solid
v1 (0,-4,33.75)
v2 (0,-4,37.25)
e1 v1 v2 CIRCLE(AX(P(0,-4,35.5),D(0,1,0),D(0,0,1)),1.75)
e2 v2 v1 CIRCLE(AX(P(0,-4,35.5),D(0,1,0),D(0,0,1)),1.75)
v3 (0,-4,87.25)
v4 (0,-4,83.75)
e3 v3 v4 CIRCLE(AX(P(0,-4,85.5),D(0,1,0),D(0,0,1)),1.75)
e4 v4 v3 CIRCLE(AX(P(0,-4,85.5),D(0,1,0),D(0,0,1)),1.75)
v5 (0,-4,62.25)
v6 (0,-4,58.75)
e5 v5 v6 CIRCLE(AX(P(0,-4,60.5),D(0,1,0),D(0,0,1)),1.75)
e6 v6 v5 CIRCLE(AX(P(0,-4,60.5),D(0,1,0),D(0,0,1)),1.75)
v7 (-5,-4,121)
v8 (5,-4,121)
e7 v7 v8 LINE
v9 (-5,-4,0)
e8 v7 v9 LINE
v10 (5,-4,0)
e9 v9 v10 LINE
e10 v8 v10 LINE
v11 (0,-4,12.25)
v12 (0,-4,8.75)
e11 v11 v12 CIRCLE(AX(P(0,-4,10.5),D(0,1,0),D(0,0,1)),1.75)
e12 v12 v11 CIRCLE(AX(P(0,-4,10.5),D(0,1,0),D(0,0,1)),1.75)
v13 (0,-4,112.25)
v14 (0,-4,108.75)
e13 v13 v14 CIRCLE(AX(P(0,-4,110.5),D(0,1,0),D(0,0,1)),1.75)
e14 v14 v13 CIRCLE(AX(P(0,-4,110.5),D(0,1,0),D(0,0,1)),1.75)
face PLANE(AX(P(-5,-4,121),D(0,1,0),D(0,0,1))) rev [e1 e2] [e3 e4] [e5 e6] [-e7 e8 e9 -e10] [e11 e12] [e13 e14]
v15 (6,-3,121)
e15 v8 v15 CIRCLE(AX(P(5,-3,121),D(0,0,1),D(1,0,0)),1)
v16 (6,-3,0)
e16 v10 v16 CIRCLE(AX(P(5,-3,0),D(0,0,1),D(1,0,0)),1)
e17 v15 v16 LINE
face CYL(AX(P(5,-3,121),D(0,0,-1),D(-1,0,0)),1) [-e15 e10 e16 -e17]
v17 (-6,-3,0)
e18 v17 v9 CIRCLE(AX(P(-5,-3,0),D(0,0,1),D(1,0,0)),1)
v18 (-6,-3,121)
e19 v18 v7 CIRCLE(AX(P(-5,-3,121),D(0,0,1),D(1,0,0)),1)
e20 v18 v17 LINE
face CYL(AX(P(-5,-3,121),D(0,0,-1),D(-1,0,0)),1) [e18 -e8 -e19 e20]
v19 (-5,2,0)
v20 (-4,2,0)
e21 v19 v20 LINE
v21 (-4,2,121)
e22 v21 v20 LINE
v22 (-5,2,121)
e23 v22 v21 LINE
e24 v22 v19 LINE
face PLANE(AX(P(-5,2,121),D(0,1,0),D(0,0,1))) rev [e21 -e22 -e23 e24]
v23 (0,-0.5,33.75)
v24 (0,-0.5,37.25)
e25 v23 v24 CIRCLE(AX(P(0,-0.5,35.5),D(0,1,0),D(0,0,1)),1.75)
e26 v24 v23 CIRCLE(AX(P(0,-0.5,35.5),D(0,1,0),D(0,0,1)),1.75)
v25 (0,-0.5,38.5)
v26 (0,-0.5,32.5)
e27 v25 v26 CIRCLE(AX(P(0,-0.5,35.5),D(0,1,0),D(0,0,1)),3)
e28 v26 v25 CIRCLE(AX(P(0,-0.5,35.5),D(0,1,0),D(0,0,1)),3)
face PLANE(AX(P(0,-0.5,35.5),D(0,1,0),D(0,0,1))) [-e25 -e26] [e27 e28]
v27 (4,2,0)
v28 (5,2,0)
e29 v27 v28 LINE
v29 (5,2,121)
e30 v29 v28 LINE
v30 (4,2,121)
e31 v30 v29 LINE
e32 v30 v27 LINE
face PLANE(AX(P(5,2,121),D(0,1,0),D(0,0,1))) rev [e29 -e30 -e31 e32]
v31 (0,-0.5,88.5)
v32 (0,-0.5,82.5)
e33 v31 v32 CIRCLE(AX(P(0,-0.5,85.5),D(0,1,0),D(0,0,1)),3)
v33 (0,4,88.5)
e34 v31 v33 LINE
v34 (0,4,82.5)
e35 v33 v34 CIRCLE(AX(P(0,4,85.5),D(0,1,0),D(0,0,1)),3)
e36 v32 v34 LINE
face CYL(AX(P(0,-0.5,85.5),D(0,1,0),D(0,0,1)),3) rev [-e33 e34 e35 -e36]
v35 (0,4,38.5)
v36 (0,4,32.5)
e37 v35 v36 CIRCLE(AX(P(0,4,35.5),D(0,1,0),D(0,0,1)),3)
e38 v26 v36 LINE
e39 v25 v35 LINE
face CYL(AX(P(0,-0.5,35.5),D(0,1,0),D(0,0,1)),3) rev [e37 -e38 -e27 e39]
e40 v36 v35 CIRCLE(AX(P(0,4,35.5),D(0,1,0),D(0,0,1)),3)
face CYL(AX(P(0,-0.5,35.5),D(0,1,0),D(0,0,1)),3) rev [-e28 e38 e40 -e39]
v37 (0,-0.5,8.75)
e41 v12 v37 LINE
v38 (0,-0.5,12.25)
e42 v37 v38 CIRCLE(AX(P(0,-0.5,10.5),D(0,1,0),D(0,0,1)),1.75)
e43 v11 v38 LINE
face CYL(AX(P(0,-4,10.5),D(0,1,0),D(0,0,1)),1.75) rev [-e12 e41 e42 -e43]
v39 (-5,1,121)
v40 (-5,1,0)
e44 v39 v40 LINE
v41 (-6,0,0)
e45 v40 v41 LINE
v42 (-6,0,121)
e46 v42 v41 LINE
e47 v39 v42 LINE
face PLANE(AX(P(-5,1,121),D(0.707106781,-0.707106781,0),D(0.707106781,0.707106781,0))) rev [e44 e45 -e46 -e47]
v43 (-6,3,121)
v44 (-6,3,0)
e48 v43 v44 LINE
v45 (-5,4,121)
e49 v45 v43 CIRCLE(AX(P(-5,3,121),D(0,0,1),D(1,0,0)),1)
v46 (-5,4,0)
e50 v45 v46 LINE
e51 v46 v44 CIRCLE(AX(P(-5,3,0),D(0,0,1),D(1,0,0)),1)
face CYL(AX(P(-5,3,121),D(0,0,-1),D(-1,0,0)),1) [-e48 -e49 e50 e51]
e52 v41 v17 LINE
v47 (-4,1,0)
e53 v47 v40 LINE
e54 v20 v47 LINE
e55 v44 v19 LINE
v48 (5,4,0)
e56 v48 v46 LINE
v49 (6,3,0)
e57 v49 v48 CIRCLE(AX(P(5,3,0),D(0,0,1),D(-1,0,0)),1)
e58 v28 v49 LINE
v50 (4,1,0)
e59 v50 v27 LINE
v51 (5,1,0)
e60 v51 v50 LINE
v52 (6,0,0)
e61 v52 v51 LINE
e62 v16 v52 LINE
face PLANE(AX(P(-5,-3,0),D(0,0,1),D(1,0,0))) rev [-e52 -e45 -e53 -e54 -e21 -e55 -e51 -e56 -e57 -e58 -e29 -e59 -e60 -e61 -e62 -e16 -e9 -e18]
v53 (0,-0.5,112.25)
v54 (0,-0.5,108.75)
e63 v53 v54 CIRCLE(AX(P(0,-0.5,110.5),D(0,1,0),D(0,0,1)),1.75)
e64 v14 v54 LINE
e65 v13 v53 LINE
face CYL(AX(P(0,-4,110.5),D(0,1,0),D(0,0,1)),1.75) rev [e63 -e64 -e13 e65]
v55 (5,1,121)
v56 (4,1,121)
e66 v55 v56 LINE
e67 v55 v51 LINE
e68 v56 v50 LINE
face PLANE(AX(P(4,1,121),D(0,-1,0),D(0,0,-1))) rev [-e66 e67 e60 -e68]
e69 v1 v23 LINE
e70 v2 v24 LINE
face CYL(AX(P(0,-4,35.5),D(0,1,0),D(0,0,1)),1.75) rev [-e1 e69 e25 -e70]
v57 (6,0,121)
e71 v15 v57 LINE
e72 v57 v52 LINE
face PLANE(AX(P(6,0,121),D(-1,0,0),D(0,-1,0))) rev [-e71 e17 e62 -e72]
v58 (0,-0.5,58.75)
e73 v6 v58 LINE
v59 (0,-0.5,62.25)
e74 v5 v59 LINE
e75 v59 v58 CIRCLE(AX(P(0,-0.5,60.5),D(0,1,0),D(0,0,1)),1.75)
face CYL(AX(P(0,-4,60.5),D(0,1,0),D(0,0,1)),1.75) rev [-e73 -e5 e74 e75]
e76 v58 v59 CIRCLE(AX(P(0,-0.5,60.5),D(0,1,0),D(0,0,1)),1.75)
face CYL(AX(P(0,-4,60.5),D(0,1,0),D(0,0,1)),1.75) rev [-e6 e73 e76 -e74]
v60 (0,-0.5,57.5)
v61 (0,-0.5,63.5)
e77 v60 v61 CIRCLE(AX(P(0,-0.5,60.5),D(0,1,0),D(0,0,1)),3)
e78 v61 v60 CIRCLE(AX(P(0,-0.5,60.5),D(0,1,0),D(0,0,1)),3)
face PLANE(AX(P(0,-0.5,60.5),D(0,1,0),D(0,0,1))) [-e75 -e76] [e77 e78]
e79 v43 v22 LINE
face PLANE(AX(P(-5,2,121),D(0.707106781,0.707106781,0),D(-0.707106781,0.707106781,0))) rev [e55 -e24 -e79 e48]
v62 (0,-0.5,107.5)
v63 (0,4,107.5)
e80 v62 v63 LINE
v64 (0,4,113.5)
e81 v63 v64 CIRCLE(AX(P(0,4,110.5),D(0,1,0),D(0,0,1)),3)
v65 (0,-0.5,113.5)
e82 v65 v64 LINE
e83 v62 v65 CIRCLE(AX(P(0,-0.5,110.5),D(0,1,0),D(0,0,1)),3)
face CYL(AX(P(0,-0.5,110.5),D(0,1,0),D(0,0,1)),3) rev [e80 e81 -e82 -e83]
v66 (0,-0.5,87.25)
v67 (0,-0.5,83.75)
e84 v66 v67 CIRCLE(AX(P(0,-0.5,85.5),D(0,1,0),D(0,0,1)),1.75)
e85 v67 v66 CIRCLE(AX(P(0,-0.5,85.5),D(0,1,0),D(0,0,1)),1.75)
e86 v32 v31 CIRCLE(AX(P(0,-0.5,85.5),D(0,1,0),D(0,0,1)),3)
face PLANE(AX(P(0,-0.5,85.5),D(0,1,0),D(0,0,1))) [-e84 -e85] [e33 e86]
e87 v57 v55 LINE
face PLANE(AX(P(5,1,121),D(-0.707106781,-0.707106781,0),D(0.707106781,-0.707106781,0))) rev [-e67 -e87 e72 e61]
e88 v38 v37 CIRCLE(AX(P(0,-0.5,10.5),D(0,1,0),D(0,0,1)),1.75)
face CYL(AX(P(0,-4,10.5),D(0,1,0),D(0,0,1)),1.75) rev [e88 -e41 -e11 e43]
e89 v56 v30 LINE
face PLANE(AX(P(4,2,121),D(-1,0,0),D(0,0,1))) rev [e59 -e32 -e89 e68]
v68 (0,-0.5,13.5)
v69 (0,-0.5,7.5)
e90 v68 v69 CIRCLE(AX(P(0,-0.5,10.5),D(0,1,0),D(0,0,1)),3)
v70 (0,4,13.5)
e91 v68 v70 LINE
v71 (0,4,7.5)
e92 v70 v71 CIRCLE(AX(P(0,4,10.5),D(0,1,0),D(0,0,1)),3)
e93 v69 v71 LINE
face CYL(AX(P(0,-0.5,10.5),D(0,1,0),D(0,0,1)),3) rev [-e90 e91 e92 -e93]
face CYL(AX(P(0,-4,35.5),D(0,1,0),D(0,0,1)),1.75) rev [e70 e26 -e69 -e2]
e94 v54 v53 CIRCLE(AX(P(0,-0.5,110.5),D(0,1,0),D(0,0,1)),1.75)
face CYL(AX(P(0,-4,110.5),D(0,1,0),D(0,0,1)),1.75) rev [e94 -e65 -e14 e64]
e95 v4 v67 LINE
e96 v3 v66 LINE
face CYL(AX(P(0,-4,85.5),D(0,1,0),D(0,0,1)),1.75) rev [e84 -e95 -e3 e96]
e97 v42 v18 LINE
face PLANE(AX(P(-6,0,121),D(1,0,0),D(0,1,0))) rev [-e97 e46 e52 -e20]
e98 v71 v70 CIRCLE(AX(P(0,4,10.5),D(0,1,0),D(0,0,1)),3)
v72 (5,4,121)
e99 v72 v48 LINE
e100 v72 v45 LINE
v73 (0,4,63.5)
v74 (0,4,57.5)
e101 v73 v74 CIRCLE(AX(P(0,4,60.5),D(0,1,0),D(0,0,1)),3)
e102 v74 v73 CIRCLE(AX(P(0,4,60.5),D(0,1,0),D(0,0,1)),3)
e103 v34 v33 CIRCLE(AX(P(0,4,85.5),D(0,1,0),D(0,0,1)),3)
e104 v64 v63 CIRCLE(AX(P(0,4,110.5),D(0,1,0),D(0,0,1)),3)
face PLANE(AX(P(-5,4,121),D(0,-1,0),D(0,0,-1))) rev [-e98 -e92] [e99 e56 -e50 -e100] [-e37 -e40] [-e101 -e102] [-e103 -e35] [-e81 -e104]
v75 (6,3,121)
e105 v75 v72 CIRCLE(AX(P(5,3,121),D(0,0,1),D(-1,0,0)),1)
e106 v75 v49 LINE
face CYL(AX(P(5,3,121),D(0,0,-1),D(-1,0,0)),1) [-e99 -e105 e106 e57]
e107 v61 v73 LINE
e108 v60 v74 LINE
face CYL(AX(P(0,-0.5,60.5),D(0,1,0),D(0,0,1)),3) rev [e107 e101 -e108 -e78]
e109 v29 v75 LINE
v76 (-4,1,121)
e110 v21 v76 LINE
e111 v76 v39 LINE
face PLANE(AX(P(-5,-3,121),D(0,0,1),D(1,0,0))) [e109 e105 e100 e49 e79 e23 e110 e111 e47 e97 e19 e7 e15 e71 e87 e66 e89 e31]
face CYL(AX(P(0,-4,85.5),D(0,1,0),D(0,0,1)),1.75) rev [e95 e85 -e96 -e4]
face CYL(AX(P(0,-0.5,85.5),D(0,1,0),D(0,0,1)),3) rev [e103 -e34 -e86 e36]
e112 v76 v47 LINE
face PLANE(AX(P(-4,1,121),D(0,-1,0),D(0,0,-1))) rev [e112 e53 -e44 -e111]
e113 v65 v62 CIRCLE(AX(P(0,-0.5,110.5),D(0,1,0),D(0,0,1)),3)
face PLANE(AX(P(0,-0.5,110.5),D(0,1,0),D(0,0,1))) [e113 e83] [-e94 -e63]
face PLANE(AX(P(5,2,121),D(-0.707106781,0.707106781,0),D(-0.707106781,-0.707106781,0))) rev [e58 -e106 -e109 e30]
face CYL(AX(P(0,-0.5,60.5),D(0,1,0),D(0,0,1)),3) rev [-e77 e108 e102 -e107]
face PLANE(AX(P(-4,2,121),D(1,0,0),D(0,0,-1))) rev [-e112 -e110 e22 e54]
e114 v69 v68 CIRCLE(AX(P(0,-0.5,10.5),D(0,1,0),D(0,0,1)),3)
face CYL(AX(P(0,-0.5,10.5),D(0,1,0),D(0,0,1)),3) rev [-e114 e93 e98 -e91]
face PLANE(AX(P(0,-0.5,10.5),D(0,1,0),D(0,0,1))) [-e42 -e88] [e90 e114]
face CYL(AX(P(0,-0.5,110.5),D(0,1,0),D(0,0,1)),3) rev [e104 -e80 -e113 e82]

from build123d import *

# Parameters (mm, degrees)
BOSS_EXTRUDE1_DEPTH = 121
SKETCH2_R           = 3
CUT_EXTRUDE1_DEPTH  = 4.5
SKETCH3_R           = 1.75
CUT_EXTRUDE2_DEPTH  = 122.232215191


with BuildPart() as part:
    # Sketch1 → Boss-Extrude1 (new body)
    with BuildSketch(Plane.XY):
        with BuildLine():
            Line((-5, 4), (5, 4))
            ThreePointArc((5, 4), (5.707106781, 3.707106781), (6, 3))
            Line((6, 3), (5, 2))
            Line((5, 2), (4, 2))
            Line((4, 2), (4, 1))
            Line((4, 1), (5, 1))
            Line((5, 1), (6, 0))
            Line((6, 0), (6, -3))
            ThreePointArc((6, -3), (5.707106781, -3.707106781), (5, -4))
            Line((5, -4), (-5, -4))
            ThreePointArc((-5, -4), (-5.707106781, -3.707106781), (-6, -3))
            Line((-6, -3), (-6, 0))
            Line((-6, 0), (-5, 1))
            Line((-5, 1), (-4, 1))
            Line((-4, 1), (-4, 2))
            Line((-4, 2), (-5, 2))
            Line((-5, 2), (-6, 3))
            ThreePointArc((-6, 3), (-5.707106781, 3.707106781), (-5, 4))
        make_face()
    extrude(amount=BOSS_EXTRUDE1_DEPTH)

    # Sketch2 → Cut-Extrude1 (cut)
    with BuildSketch(Plane(origin=(0, 4, 0), x_dir=(1, 0, 0), z_dir=(0, 1, 0))):
        with Locations(Location((0, -10.5, 0), (0, 0, 270))):
            Circle(SKETCH2_R)
        with Locations(Location((0, -35.5, 0), (0, 0, 270))):
            Circle(SKETCH2_R)
        with Locations(Location((0, -60.5, 0), (0, 0, 270))):
            Circle(SKETCH2_R)
        with Locations(Location((0, -85.5, 0), (0, 0, 270))):
            Circle(SKETCH2_R)
        with Locations(Location((0, -110.5, 0), (0, 0, 270))):
            Circle(SKETCH2_R)
    extrude(amount=-CUT_EXTRUDE1_DEPTH, mode=Mode.SUBTRACT)

    # Sketch3 → Cut-Extrude2 (cut, through all)
    with BuildSketch(Plane(origin=(0, -0.5, 0), x_dir=(1, 0, 0), z_dir=(0, 1, 0))):
        with Locations(Location((0, -35.5, 0), (0, 0, 270))):
            Circle(SKETCH3_R)
        with Locations(Location((0, -10.5, 0), (0, 0, 270))):
            Circle(SKETCH3_R)
        with Locations(Location((0, -60.5, 0), (0, 0, 270))):
            Circle(SKETCH3_R)
        with Locations(Location((0, -85.5, 0), (0, 0, 270))):
            Circle(SKETCH3_R)
        with Locations(Location((0, -110.5, 0), (0, 0, 270))):
            Circle(SKETCH3_R)
    extrude(amount=-CUT_EXTRUDE2_DEPTH, mode=Mode.SUBTRACT)


solid = part.part
